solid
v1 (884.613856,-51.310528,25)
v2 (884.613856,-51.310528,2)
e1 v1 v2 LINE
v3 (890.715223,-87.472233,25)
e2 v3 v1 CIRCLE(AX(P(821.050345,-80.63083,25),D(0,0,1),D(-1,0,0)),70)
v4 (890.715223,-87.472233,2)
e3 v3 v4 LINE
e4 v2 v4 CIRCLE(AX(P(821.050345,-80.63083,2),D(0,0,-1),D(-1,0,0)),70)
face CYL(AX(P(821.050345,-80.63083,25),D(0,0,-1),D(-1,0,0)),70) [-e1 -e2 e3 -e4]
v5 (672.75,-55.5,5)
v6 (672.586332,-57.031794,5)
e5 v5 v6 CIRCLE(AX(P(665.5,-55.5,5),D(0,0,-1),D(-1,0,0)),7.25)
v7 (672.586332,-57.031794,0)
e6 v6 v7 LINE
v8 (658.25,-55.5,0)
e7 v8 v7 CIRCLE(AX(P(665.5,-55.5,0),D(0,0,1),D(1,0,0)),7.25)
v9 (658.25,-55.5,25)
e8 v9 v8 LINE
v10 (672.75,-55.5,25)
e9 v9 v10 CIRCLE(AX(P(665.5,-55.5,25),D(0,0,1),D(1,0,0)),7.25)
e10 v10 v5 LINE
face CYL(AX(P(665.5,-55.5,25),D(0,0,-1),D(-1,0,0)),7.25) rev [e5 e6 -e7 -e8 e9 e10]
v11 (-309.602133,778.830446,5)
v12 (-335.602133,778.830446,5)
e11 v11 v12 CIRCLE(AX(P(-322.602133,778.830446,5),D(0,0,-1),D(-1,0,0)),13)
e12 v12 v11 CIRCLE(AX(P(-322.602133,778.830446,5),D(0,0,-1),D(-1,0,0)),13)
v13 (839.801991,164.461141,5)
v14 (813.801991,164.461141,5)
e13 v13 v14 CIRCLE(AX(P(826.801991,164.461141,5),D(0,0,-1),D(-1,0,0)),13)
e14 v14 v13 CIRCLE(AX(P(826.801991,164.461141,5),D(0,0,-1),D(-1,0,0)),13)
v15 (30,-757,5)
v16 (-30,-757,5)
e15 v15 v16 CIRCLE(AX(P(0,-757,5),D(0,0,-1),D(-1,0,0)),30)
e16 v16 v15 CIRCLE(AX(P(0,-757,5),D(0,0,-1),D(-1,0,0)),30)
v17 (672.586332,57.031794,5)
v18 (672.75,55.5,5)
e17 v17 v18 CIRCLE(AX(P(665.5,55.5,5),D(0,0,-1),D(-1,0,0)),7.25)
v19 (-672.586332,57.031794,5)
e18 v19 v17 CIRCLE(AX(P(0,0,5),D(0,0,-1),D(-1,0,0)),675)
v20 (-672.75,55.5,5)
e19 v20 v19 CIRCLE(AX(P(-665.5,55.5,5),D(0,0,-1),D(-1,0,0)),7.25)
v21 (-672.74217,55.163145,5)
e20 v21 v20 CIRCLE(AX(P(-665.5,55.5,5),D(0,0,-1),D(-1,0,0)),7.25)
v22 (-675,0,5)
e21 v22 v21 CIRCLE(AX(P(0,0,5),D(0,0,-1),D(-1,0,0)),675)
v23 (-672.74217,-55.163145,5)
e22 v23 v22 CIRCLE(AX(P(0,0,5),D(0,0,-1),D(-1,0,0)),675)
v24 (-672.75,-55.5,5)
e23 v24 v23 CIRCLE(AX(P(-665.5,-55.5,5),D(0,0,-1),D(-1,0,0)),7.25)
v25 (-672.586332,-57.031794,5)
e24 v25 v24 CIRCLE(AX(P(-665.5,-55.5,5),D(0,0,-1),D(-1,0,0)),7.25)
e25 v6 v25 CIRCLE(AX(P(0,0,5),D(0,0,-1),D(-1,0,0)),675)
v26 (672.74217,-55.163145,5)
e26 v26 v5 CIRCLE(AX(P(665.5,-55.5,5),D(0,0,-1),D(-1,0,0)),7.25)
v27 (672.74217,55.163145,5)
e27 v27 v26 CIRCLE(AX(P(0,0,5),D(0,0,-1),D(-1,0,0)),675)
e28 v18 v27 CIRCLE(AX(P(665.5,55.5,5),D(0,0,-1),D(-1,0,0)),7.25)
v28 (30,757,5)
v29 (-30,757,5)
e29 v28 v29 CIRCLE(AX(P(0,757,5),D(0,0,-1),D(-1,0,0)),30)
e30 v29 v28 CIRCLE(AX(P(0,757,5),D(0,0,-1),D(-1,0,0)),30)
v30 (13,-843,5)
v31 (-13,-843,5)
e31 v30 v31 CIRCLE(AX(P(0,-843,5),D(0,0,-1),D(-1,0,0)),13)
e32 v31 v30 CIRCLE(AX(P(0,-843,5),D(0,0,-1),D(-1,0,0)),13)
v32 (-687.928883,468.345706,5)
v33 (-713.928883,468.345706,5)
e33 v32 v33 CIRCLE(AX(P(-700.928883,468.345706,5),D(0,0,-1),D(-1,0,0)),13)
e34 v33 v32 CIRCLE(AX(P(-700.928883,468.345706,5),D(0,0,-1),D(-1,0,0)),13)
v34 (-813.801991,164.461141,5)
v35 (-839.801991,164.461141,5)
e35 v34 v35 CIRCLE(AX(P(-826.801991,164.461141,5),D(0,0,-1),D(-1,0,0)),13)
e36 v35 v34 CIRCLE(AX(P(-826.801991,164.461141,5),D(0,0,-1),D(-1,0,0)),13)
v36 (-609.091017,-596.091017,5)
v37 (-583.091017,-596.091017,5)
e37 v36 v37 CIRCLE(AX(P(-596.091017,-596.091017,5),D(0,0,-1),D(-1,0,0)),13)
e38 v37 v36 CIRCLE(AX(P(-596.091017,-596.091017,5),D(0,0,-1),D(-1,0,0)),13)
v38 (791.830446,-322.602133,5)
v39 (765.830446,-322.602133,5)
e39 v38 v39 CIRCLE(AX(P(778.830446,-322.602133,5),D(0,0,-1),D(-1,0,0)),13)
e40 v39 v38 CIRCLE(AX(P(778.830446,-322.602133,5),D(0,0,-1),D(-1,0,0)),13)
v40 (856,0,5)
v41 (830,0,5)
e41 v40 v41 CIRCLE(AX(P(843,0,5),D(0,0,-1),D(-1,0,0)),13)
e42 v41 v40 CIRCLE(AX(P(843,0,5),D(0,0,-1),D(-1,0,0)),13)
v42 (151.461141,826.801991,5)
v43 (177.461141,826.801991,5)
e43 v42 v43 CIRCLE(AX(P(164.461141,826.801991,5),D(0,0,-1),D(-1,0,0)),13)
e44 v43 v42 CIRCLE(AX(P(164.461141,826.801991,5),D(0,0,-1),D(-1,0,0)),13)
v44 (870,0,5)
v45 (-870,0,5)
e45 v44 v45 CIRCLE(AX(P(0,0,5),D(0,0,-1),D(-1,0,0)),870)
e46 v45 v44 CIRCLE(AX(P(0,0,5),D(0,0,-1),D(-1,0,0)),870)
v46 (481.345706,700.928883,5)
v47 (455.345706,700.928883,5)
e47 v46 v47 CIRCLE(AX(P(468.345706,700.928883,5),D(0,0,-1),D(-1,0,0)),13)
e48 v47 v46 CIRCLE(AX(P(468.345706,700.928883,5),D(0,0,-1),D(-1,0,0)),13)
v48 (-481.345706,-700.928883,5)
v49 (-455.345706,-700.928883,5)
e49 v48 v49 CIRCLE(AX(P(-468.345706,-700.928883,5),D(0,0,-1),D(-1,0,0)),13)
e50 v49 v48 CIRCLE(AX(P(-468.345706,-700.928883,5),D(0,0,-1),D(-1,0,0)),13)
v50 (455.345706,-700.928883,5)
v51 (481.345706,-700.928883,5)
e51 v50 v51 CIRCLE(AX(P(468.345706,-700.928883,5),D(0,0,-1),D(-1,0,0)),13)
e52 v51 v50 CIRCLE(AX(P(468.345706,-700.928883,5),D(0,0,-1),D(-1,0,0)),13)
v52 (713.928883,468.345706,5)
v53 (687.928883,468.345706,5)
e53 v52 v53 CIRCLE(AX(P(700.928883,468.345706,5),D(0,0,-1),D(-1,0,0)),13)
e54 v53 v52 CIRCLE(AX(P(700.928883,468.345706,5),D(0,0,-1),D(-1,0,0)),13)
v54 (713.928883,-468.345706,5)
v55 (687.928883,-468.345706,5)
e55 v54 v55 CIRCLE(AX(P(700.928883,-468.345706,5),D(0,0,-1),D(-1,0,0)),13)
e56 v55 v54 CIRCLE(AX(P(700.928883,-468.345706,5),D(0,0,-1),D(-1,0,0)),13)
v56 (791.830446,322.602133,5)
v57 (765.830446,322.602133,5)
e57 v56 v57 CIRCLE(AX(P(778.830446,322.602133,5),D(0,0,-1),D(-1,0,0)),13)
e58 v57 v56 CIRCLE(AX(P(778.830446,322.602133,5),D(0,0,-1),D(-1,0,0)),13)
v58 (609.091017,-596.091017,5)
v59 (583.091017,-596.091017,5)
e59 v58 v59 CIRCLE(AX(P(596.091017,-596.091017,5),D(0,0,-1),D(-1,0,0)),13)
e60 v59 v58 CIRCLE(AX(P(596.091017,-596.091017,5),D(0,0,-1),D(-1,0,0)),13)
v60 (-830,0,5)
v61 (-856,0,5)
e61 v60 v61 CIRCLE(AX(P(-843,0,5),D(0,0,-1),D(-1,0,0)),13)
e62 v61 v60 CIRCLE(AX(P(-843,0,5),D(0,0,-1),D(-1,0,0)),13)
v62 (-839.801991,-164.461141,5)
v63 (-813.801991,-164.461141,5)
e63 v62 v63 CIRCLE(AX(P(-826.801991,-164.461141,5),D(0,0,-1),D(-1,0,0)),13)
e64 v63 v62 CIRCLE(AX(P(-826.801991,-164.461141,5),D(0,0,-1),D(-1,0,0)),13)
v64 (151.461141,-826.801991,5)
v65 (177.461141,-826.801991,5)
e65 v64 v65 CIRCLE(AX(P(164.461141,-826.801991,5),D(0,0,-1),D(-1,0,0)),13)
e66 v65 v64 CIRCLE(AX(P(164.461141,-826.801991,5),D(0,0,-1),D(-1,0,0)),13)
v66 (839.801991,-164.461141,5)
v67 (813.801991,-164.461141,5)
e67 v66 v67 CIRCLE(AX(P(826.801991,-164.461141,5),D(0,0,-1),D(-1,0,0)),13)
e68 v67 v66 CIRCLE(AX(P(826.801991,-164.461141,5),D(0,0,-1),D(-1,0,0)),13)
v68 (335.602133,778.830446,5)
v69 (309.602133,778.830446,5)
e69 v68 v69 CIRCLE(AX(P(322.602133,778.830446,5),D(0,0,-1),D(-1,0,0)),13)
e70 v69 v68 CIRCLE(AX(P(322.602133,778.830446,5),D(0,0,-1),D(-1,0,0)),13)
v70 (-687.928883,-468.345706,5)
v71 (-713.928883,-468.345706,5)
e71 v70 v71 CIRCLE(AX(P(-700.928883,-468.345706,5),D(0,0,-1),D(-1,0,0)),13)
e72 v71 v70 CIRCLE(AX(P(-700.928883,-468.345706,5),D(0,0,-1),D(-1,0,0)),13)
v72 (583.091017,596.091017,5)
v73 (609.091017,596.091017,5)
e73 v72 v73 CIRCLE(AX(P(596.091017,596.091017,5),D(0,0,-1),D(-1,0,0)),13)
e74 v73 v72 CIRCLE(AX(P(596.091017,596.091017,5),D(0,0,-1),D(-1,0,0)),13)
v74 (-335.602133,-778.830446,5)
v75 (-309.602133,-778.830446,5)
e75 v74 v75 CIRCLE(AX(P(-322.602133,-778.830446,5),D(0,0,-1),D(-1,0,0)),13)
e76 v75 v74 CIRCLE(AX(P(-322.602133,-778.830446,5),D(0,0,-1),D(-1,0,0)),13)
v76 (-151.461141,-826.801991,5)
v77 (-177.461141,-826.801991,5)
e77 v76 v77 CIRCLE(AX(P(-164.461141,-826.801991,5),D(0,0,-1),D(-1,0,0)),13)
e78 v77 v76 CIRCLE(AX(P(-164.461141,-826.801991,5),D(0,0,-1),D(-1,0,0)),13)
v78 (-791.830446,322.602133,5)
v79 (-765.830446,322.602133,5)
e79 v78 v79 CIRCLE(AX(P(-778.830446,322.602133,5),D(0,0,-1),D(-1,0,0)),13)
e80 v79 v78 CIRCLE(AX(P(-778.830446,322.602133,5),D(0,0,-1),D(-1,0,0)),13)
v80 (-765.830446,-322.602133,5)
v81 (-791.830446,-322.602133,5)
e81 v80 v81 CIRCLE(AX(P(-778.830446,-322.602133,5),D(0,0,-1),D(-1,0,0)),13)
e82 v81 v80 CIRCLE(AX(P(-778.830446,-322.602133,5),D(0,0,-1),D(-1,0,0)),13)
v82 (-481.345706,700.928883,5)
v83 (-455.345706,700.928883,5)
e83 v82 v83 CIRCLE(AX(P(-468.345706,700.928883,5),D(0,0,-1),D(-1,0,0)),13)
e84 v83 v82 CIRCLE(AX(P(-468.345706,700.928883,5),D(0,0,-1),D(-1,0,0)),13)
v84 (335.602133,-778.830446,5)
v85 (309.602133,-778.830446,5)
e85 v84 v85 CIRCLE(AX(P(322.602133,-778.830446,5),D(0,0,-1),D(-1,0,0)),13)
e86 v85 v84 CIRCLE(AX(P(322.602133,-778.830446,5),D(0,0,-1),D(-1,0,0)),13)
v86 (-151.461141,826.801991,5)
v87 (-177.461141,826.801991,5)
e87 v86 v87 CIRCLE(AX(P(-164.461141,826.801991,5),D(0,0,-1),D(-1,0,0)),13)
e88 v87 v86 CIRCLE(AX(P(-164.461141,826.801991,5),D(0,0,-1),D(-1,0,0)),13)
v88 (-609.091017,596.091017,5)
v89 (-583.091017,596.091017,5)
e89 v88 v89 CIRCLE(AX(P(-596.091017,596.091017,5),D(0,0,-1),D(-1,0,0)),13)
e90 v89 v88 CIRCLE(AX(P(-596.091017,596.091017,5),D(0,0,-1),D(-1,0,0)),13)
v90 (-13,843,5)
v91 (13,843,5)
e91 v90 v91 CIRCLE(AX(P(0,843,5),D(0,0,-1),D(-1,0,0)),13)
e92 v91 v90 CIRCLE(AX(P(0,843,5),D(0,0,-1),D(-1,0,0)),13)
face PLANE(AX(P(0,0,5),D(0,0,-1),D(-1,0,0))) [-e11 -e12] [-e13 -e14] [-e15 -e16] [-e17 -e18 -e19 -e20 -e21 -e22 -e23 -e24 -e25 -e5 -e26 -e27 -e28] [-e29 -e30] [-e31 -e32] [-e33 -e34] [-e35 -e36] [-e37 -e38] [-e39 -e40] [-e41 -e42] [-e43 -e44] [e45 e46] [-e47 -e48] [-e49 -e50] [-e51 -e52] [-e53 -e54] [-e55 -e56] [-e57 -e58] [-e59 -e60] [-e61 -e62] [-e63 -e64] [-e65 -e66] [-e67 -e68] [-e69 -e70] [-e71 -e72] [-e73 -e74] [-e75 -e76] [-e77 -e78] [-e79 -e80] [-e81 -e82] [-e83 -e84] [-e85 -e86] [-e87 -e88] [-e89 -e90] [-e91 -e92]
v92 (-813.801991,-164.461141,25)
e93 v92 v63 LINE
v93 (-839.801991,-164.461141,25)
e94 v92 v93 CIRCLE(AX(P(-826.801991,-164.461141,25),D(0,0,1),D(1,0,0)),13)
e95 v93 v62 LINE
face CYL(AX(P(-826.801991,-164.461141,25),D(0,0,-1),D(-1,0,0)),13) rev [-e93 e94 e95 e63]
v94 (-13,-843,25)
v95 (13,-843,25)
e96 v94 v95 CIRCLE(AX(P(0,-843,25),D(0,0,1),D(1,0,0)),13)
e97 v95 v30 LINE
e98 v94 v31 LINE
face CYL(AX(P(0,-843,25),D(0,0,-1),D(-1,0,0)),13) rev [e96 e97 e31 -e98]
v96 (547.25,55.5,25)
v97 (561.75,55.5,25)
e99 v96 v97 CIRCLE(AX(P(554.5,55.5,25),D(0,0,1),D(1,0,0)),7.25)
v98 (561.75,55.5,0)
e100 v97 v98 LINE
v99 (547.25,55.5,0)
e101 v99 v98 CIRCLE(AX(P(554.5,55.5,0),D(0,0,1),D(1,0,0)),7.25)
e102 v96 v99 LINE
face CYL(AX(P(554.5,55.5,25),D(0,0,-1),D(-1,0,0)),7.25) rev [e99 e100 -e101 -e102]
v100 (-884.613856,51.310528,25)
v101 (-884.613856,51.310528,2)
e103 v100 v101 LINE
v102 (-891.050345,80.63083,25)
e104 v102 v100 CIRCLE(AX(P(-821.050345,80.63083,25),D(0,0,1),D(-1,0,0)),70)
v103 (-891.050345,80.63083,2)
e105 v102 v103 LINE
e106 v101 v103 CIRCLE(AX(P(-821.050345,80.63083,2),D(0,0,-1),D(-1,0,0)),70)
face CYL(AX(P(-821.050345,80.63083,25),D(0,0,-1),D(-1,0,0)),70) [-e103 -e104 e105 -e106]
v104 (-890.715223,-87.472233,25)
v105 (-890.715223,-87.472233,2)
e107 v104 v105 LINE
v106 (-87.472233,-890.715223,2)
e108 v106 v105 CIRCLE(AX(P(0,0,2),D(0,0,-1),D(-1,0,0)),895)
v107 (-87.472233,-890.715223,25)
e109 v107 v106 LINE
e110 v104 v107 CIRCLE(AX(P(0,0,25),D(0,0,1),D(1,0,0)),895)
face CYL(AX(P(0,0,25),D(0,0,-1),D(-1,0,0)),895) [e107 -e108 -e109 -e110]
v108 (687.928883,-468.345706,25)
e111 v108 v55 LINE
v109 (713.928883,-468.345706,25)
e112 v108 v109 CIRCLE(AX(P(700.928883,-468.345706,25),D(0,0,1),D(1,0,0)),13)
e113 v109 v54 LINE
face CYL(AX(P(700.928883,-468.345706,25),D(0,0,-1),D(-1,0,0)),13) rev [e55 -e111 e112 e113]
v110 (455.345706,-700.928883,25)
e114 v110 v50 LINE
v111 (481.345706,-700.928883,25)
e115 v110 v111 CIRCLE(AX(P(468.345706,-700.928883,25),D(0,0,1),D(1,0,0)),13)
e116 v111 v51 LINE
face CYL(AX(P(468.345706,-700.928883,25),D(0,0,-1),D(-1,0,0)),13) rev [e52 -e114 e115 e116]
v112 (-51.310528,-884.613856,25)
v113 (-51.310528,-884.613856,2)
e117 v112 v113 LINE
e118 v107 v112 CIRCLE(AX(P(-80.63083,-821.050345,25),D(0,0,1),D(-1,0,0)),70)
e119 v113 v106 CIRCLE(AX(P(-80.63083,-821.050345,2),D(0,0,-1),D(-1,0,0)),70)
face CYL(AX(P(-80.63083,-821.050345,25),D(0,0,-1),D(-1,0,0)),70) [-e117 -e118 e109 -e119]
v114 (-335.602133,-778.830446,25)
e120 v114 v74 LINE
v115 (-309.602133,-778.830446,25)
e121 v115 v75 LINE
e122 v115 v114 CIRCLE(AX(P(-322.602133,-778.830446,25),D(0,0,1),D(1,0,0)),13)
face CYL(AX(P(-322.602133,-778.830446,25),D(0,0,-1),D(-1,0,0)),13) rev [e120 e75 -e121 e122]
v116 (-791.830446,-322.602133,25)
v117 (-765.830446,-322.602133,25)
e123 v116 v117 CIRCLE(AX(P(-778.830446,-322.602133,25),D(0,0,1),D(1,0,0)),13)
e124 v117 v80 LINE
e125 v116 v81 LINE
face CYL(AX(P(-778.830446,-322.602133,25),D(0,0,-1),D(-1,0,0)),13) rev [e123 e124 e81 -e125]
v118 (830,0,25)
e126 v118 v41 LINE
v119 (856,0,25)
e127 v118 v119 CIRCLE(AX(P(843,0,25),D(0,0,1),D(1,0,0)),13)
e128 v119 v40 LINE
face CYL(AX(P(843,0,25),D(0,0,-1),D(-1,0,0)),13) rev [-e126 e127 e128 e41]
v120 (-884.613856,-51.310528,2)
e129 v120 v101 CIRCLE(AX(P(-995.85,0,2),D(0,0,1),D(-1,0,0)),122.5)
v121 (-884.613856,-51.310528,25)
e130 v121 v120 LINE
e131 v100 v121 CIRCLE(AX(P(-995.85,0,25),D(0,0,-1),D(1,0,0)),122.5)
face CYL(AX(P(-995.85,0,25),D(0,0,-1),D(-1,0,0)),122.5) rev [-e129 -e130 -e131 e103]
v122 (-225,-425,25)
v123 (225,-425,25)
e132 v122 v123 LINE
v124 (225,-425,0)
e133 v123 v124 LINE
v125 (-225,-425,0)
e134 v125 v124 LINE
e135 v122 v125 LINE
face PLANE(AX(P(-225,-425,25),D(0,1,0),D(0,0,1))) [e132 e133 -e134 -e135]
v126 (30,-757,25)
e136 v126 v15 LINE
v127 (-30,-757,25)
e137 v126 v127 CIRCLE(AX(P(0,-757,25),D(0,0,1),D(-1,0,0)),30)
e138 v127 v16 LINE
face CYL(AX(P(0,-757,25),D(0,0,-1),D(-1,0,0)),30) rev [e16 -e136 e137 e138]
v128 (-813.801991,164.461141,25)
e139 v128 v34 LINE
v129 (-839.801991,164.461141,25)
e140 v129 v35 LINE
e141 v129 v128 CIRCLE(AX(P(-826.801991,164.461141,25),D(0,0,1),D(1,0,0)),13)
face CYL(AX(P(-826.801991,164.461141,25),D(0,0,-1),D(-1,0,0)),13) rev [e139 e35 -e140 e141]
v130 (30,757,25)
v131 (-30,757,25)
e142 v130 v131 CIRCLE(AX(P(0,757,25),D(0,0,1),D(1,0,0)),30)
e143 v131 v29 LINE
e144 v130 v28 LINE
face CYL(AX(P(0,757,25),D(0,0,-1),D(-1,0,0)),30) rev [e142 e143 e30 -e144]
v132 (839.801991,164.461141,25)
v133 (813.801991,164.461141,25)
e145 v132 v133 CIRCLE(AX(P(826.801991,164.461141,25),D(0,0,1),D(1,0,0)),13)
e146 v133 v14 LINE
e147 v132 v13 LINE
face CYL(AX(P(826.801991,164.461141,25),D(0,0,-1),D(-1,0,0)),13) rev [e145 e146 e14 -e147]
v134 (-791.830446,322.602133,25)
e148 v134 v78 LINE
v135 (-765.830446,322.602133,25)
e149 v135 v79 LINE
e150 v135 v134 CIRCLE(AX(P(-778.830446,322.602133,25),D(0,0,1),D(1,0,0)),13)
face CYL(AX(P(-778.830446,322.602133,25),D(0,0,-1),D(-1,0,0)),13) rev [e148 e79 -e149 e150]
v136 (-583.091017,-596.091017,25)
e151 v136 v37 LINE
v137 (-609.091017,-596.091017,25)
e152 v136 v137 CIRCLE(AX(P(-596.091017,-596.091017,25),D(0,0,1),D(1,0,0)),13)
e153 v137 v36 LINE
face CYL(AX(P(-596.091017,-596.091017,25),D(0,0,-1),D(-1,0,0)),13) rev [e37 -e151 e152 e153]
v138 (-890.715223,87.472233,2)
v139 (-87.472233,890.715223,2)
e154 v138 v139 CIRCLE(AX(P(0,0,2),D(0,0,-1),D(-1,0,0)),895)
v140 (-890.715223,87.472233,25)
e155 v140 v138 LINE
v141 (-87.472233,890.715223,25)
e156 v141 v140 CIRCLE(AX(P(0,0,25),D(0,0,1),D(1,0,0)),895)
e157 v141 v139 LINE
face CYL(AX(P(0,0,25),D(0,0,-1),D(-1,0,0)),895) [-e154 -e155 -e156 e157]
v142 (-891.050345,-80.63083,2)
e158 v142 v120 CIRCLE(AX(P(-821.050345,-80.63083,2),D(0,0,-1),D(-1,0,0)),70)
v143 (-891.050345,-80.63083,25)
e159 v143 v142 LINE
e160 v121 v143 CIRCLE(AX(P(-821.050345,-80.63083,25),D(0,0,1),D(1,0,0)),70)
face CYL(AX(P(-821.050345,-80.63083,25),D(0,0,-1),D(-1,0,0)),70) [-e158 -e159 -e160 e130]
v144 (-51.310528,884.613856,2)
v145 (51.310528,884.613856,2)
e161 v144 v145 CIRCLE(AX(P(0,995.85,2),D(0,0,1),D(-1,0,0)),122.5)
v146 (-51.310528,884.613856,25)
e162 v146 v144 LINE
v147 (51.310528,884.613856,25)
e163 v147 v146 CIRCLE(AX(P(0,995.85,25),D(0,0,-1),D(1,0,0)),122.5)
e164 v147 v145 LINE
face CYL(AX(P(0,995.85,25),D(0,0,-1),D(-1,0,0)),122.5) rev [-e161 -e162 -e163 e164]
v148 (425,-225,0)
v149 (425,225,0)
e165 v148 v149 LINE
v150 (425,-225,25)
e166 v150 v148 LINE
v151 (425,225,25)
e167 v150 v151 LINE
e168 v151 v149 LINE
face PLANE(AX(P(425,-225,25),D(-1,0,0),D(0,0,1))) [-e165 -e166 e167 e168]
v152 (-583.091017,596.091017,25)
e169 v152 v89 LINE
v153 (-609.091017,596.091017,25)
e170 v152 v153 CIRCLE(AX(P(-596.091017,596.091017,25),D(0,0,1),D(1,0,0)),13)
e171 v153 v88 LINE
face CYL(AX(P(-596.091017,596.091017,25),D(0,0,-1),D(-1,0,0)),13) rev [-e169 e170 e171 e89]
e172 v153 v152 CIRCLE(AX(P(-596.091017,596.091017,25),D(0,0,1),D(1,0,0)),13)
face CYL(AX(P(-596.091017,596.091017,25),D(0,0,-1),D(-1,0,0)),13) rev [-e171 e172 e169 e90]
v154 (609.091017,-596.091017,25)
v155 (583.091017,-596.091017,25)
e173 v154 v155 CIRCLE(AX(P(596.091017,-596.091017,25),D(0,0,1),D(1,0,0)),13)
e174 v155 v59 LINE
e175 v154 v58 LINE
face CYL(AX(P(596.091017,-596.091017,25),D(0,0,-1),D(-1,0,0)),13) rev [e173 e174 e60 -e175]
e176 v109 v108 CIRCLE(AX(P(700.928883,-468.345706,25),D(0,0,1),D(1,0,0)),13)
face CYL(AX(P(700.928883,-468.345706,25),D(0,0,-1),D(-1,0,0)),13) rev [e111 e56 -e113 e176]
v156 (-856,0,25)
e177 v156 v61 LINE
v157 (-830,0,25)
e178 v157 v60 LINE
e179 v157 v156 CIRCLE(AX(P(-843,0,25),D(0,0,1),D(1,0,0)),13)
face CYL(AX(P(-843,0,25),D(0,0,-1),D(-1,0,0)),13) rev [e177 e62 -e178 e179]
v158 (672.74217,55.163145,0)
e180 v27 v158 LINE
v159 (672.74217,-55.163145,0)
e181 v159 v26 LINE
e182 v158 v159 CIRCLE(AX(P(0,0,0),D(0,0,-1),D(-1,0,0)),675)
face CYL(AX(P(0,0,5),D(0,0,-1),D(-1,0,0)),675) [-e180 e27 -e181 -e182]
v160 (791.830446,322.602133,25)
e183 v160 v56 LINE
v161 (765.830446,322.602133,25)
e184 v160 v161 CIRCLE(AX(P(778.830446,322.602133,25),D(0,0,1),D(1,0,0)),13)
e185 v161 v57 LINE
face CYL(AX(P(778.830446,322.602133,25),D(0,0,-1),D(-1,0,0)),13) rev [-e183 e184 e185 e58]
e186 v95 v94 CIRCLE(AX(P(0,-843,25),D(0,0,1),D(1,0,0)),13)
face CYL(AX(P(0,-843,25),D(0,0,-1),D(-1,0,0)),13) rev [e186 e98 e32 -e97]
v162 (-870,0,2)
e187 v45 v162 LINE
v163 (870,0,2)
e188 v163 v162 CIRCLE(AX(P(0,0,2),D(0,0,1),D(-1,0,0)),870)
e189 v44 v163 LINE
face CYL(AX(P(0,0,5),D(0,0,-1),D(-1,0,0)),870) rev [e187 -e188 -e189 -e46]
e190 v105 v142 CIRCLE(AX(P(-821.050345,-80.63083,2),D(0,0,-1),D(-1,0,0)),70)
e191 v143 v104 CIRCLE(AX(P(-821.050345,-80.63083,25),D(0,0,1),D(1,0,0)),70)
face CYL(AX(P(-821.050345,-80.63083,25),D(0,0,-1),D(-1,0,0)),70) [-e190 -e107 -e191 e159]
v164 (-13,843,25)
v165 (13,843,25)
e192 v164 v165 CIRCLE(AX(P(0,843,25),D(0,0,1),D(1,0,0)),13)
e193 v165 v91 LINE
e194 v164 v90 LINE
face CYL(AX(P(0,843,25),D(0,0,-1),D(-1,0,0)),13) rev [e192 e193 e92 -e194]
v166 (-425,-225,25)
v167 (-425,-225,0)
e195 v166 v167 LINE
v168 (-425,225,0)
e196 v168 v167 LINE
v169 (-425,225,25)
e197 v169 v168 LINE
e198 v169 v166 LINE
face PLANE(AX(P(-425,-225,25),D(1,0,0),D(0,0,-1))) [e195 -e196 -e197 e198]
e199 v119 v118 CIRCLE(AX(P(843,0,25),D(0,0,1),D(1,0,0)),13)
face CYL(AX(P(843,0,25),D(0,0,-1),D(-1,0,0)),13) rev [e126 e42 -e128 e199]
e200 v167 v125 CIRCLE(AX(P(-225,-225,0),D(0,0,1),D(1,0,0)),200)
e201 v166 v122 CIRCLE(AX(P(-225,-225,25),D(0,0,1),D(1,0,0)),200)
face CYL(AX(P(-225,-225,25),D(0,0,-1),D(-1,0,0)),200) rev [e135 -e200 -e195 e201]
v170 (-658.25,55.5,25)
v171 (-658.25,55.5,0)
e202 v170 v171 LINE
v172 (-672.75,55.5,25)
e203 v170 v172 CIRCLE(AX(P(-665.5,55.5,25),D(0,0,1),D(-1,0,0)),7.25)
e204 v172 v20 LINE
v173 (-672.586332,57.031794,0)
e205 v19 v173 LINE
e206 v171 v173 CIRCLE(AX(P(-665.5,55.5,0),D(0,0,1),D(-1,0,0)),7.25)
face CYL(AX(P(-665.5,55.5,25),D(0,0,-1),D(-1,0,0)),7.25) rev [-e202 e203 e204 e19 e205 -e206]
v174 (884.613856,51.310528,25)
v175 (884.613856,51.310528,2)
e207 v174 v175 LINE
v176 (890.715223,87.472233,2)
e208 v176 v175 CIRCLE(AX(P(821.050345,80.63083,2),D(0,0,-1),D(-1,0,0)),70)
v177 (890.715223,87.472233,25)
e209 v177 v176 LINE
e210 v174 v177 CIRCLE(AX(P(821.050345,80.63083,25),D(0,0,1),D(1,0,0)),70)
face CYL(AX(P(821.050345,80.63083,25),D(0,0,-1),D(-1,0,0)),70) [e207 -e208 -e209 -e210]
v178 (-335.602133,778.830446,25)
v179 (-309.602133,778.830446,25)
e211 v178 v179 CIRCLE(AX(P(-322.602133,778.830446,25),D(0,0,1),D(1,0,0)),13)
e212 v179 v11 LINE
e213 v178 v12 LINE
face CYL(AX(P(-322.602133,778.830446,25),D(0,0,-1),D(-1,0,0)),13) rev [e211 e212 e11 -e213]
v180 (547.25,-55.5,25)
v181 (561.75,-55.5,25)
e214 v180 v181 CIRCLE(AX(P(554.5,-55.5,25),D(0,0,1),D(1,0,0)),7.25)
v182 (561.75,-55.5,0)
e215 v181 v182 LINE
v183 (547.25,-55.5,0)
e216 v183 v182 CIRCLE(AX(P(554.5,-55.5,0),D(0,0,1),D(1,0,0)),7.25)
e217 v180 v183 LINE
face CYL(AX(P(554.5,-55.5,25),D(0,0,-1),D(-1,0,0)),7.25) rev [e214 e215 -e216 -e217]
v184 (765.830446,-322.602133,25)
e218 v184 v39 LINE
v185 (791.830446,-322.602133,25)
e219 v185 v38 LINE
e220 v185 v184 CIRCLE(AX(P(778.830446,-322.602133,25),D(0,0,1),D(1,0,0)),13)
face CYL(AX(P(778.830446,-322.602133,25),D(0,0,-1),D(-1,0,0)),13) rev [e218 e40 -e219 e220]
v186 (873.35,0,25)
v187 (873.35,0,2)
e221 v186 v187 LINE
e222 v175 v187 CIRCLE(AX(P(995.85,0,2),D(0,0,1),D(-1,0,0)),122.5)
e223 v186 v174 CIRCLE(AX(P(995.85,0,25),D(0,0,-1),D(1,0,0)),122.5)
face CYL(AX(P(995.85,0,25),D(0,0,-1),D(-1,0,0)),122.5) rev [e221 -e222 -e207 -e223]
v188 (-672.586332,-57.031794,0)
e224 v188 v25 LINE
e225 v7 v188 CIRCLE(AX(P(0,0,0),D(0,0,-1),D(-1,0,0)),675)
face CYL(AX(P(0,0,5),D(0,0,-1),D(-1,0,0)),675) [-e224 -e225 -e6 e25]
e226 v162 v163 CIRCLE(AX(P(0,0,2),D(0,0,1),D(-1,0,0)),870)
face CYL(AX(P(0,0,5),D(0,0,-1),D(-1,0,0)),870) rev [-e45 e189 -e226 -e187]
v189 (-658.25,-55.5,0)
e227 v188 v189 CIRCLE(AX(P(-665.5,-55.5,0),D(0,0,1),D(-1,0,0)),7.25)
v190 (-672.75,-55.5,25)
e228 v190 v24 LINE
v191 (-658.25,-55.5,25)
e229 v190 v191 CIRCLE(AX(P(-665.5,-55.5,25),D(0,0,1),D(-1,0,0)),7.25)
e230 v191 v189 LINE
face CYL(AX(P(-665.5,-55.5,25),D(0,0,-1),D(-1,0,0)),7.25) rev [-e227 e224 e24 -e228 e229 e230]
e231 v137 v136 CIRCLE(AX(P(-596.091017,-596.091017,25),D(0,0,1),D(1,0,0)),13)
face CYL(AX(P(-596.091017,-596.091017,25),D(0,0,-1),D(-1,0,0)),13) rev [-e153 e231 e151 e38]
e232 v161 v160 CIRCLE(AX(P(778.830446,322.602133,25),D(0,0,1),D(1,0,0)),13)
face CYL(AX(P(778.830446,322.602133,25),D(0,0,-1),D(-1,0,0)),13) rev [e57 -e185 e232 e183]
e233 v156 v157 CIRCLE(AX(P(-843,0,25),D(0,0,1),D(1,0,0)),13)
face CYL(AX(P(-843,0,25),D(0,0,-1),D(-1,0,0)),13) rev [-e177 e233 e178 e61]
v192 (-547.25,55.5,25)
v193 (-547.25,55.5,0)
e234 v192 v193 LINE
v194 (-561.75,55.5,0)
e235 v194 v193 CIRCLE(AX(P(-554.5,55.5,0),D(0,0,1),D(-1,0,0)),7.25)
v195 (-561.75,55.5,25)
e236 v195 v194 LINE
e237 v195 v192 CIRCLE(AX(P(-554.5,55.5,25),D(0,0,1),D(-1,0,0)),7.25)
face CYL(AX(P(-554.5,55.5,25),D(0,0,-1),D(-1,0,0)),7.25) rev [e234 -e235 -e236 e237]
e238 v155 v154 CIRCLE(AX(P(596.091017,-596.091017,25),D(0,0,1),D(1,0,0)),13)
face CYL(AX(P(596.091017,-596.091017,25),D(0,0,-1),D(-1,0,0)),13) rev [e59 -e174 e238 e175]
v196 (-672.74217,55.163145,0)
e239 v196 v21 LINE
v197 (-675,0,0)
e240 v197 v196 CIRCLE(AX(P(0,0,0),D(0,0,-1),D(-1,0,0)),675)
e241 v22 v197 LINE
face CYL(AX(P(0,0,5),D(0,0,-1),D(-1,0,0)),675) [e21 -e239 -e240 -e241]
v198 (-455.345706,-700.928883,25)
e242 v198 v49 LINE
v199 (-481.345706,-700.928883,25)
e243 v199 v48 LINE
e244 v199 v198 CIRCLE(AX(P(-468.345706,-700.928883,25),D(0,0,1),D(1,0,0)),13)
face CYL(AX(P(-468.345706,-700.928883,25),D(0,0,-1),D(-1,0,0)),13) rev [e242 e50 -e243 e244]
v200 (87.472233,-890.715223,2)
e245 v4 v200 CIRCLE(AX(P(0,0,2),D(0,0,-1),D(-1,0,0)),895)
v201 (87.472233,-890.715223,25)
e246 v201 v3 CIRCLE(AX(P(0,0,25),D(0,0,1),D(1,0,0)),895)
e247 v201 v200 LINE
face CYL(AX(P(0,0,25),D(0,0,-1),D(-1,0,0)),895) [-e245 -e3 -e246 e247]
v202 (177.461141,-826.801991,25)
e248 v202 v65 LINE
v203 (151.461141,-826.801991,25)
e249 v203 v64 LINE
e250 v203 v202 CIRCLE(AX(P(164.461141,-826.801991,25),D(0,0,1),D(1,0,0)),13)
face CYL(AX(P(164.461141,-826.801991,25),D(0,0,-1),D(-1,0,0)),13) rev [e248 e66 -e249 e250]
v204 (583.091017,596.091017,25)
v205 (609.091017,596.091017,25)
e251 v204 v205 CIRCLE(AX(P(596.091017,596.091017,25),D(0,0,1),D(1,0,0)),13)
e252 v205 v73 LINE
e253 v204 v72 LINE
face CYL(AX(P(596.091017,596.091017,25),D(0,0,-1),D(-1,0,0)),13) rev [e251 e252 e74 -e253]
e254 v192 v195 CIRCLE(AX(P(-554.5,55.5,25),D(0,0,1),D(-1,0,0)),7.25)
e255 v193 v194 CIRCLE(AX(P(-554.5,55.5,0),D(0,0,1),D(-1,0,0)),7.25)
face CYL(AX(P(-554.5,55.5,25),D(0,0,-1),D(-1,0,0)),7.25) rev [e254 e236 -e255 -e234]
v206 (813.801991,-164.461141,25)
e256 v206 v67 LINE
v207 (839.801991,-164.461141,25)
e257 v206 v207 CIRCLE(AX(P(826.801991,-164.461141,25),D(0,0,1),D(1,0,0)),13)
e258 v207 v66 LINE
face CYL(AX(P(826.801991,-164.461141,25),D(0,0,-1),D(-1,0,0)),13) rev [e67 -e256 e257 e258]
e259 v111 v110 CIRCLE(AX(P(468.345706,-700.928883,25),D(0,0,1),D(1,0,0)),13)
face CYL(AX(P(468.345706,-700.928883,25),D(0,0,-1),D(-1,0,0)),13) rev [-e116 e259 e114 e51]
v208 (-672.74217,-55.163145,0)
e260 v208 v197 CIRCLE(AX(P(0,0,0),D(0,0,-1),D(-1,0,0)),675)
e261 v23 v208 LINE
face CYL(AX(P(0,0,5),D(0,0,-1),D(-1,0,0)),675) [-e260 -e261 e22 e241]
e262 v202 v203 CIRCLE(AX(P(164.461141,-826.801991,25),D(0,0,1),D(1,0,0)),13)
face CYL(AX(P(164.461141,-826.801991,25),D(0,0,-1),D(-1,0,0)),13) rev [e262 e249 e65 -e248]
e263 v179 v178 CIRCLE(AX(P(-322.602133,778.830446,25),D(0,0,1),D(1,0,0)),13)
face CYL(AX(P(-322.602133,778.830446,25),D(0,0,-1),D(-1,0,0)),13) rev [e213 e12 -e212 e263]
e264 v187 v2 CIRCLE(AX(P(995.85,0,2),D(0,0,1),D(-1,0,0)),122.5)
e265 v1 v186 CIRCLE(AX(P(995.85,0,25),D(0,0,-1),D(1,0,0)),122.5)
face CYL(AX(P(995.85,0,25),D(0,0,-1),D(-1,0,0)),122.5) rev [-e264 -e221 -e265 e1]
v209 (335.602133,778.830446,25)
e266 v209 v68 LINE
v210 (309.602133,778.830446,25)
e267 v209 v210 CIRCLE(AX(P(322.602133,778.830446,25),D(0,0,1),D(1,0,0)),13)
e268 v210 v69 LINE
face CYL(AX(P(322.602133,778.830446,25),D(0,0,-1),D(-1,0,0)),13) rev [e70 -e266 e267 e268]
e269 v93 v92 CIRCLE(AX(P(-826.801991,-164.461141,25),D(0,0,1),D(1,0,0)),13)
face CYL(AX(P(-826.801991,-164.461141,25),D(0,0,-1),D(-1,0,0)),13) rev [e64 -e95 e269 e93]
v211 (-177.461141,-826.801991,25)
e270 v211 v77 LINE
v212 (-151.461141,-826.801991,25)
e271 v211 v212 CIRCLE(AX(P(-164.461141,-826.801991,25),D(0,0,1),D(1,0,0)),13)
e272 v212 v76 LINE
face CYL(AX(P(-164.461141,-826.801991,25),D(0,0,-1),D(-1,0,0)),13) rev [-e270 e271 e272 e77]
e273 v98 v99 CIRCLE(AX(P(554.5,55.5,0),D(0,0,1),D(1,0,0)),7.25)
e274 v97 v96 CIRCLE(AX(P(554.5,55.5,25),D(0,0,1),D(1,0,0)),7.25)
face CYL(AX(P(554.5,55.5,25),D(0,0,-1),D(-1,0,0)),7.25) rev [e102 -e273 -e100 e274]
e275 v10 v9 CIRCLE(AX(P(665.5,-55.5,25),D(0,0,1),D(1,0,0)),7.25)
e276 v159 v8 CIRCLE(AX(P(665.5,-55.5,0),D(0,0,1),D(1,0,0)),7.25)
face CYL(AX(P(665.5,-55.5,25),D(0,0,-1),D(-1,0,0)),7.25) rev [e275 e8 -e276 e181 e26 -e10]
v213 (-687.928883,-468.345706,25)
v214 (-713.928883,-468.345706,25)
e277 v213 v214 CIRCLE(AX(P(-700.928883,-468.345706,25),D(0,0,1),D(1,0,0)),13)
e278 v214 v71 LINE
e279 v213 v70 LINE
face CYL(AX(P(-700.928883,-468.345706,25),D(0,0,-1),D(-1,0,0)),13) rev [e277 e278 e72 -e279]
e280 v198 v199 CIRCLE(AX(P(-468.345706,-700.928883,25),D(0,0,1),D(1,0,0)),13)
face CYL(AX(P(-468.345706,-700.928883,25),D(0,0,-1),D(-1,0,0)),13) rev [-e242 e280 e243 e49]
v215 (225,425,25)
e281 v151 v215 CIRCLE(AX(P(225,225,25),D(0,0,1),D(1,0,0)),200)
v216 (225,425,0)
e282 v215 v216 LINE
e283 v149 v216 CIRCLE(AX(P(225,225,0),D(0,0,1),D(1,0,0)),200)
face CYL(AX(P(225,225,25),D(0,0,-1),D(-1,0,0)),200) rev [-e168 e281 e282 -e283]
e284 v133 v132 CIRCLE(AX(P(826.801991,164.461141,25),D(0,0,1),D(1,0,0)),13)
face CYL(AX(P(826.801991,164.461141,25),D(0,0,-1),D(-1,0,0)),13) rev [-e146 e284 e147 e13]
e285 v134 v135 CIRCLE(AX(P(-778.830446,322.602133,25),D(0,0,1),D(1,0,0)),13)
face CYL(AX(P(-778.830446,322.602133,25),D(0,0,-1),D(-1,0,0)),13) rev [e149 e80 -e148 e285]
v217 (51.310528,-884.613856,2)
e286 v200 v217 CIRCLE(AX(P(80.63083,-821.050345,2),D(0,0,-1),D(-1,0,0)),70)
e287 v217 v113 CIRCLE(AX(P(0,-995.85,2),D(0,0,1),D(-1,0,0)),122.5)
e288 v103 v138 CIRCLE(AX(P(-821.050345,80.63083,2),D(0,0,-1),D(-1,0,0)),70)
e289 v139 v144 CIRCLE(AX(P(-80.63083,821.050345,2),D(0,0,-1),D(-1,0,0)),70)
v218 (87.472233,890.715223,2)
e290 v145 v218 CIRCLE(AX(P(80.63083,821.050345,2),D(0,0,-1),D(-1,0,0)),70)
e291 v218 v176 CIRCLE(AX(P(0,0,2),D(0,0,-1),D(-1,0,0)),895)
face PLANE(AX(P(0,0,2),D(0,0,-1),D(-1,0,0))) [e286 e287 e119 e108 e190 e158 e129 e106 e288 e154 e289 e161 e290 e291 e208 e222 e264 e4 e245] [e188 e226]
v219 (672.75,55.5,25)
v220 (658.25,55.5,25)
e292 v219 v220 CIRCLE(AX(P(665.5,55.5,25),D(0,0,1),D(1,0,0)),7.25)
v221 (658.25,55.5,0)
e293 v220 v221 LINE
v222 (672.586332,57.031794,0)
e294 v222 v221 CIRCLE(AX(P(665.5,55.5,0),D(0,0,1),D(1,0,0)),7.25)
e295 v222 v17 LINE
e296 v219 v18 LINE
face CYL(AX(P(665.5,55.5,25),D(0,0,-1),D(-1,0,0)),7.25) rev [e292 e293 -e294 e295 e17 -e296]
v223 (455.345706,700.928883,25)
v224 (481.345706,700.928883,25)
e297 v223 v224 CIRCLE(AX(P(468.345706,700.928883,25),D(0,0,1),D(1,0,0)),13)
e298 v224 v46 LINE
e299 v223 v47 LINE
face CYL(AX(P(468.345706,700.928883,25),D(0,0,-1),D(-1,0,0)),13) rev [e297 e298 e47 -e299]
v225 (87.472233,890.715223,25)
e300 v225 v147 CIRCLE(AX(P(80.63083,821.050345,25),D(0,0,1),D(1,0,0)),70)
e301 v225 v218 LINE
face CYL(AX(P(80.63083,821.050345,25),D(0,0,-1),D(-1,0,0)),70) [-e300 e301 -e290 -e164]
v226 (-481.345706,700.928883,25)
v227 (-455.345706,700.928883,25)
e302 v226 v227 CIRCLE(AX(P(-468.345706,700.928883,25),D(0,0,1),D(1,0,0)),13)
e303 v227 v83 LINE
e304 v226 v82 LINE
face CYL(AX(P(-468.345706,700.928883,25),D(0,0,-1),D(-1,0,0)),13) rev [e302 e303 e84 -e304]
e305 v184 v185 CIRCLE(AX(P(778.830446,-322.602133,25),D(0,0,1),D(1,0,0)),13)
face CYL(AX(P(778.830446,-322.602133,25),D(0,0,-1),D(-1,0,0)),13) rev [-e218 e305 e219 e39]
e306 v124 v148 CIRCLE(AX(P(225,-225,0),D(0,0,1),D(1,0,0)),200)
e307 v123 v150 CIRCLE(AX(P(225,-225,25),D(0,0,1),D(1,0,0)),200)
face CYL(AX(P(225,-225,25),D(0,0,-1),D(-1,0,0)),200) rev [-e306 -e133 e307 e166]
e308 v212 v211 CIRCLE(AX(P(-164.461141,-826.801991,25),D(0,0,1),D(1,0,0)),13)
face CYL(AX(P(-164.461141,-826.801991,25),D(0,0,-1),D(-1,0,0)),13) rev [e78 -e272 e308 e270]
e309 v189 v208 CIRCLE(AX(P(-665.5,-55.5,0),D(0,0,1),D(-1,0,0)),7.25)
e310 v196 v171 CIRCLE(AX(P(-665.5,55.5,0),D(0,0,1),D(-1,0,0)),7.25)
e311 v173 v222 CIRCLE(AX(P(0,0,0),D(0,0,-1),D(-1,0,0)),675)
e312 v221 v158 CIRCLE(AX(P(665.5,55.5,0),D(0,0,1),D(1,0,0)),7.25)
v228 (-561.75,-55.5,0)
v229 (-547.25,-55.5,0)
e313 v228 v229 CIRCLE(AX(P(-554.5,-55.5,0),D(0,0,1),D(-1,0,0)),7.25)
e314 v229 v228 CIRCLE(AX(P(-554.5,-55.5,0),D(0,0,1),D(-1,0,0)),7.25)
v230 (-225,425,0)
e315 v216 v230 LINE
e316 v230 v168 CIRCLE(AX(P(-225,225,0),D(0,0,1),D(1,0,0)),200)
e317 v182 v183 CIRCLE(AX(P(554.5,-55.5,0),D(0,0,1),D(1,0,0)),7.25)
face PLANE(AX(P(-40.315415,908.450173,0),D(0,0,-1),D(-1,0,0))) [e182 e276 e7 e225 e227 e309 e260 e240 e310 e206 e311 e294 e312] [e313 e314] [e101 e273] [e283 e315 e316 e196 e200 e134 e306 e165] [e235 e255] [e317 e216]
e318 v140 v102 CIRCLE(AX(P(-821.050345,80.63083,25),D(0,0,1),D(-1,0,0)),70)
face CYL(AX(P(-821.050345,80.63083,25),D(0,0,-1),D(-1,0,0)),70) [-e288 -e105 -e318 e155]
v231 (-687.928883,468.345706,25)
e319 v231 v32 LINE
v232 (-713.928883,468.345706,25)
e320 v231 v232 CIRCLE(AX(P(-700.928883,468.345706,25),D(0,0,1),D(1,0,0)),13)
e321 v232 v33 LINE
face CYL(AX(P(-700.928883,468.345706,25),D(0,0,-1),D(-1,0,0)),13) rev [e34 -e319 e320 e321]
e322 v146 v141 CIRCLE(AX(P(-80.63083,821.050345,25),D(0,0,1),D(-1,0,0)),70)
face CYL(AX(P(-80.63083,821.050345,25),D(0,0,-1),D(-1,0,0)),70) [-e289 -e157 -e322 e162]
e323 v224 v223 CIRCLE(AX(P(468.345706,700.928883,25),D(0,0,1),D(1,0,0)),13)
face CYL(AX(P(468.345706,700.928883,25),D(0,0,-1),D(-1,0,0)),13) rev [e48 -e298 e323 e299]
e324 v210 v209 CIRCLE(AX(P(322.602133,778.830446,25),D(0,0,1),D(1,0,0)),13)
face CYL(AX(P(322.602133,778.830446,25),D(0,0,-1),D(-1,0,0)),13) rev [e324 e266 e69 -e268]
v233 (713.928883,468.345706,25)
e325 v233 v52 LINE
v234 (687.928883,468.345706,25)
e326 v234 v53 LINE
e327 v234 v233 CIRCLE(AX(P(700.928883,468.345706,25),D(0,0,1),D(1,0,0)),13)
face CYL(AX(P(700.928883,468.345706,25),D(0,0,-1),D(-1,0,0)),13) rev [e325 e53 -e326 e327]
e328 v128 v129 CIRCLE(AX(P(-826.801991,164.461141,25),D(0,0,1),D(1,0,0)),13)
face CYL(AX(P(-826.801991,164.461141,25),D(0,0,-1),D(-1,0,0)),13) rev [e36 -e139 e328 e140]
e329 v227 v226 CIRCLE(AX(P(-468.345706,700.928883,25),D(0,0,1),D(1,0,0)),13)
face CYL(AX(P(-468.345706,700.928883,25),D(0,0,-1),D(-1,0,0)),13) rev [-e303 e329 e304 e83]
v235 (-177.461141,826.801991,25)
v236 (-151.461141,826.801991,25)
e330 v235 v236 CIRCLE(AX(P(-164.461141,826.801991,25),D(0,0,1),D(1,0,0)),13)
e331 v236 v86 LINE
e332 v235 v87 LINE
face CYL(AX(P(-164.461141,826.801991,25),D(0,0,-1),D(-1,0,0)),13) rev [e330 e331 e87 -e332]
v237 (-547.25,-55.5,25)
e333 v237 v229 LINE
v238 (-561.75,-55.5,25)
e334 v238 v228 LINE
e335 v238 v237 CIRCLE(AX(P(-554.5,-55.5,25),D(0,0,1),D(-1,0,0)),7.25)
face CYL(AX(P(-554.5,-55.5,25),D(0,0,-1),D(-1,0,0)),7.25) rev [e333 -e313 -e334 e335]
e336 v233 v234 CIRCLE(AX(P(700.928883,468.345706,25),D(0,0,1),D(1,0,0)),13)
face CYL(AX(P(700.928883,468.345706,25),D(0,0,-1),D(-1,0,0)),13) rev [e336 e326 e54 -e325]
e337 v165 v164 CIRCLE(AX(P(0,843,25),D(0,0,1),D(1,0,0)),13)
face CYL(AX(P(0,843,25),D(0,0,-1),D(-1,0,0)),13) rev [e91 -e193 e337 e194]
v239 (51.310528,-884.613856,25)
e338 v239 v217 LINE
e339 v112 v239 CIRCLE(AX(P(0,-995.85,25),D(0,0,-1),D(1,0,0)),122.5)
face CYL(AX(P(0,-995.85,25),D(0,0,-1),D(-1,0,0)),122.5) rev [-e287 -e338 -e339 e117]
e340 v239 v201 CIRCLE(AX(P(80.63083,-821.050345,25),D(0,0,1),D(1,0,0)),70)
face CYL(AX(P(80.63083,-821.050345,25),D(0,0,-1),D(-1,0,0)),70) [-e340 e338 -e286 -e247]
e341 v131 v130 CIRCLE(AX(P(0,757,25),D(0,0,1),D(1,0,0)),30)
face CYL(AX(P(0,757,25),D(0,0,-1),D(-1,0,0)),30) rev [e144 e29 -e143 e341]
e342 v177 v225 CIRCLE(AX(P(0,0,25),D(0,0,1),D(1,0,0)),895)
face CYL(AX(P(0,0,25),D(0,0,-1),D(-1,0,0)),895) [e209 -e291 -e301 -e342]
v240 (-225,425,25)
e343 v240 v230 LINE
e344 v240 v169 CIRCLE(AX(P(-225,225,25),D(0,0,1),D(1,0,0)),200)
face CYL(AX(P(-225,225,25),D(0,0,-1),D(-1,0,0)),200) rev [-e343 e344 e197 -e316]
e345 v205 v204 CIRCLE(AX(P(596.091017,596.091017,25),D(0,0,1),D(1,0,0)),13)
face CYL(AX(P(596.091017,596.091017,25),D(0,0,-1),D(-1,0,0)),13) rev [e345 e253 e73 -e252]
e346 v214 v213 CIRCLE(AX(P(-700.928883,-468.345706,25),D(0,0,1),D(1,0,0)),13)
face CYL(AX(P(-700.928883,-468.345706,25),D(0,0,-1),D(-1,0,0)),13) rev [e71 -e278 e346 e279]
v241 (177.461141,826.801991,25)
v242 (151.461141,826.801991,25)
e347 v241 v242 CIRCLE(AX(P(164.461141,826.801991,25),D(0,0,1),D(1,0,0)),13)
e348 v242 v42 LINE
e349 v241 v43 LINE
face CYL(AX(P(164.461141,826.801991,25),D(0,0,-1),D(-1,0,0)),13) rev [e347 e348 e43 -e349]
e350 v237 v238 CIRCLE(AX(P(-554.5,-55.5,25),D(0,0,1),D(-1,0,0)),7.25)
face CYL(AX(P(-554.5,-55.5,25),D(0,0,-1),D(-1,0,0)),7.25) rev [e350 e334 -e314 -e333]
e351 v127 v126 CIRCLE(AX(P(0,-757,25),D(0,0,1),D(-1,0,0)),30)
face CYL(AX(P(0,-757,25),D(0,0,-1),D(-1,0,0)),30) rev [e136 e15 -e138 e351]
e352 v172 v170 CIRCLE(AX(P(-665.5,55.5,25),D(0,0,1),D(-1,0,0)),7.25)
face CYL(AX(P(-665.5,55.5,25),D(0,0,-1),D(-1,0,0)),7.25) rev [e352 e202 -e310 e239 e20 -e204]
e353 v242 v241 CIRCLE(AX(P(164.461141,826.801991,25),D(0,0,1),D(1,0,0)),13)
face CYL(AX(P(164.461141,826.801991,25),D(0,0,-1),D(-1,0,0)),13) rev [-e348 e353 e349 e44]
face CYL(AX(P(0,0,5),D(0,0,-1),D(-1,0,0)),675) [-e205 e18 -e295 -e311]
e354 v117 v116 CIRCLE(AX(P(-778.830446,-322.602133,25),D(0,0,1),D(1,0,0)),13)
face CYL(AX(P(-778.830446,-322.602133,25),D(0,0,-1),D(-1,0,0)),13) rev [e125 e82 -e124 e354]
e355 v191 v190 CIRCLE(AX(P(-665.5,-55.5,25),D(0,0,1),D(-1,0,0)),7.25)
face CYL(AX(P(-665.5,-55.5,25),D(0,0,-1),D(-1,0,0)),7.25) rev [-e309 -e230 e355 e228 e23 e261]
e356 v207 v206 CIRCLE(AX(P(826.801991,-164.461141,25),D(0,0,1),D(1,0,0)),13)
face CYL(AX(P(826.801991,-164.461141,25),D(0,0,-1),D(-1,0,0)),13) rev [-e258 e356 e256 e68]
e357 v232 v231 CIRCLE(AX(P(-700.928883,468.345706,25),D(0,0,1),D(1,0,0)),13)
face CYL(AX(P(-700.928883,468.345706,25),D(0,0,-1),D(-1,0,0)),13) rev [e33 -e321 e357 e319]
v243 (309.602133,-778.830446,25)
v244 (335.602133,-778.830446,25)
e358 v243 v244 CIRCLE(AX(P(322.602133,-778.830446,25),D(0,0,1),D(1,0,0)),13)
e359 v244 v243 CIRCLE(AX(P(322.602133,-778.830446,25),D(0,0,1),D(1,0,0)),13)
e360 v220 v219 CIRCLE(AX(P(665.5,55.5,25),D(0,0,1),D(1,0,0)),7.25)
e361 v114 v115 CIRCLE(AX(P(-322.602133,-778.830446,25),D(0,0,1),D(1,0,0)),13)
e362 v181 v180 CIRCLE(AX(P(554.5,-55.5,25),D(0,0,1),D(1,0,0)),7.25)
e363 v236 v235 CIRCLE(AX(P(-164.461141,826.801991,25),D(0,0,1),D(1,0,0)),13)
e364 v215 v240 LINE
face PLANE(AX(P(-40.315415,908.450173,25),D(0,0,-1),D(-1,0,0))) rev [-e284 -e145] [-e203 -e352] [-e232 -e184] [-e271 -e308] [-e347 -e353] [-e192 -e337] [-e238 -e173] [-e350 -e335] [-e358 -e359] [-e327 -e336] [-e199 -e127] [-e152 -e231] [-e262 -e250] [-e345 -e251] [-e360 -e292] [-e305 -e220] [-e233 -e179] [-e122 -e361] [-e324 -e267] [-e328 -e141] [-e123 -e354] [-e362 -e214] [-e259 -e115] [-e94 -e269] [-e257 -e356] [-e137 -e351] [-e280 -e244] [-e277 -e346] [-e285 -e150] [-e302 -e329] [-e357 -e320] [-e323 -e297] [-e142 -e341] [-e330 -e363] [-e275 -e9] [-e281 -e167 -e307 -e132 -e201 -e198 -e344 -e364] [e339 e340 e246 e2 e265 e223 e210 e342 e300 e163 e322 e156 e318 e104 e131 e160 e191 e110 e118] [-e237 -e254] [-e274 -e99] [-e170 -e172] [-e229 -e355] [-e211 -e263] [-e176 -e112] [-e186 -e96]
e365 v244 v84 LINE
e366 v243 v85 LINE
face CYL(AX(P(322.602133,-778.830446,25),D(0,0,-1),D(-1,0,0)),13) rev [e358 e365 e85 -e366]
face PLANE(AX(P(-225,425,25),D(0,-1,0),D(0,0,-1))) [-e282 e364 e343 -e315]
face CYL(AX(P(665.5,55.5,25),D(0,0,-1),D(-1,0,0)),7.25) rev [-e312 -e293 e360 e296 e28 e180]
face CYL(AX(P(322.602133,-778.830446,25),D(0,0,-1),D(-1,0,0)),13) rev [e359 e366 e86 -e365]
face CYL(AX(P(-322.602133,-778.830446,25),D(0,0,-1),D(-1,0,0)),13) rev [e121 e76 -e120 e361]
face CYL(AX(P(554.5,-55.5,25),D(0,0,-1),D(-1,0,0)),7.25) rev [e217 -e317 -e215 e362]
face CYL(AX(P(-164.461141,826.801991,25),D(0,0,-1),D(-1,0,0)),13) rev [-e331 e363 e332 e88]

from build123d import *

# Parameters (mm, degrees)
SKETCH1_R           = 13
SKETCH1_R_2         = 30
SKETCH1_R_3         = 7.25
BOSS_EXTRUDE1_DEPTH = 25
SKETCH2_R           = 870
SKETCH2_R_2         = 675
CUT_EXTRUDE1_DEPTH  = 5
SKETCH3_R           = 1126.547936792
SKETCH3_R_2         = 762.256112449
CUT_EXTRUDE2_DEPTH  = 2


with BuildPart() as part:
    # Sketch1 → Boss-Extrude1 (new body)
    with BuildSketch(Plane.XY):
        with BuildLine():
            ThreePointArc((-87.472233281, 890.715222956), (-632.860569162, 632.860569162), (-890.715222956, 87.472233281))
            ThreePointArc((-890.715222956, 87.472233281), (-890.074747514, 68.984719363), (-884.613856025, 51.310527902))
            ThreePointArc((-884.613856025, 51.310527902), (-873.35, 0), (-884.613856025, -51.310527902))
            ThreePointArc((-884.613856025, -51.310527902), (-890.074747514, -68.984719363), (-890.715222956, -87.472233281))
            ThreePointArc((-890.715222956, -87.472233281), (-632.860569162, -632.860569162), (-87.472233281, -890.715222956))
            ThreePointArc((-87.472233281, -890.715222956), (-68.984719363, -890.074747514), (-51.310527902, -884.613856025))
            ThreePointArc((-51.310527902, -884.613856025), (0, -873.35), (51.310527902, -884.613856025))
            ThreePointArc((51.310527902, -884.613856025), (68.984719363, -890.074747514), (87.472233281, -890.715222956))
            ThreePointArc((87.472233281, -890.715222956), (632.860569162, -632.860569162), (890.715222956, -87.472233281))
            ThreePointArc((890.715222956, -87.472233281), (890.074747514, -68.984719363), (884.613856025, -51.310527902))
            ThreePointArc((884.613856025, -51.310527902), (873.35, 0), (884.613856025, 51.310527902))
            ThreePointArc((884.613856025, 51.310527902), (890.074747514, 68.984719363), (890.715222956, 87.472233281))
            ThreePointArc((890.715222956, 87.472233281), (632.860569162, 632.860569162), (87.472233281, 890.715222956))
            ThreePointArc((87.472233281, 890.715222956), (68.984719363, 890.074747514), (51.310527902, 884.613856025))
            ThreePointArc((51.310527902, 884.613856025), (0, 873.35), (-51.310527902, 884.613856025))
            ThreePointArc((-51.310527902, 884.613856025), (-68.984719363, 890.074747514), (-87.472233281, 890.715222956))
        make_face()
        with Locations((0, 843)):
            Circle(SKETCH1_R, mode=Mode.SUBTRACT)
        with Locations((0, 757)):
            Circle(SKETCH1_R_2, mode=Mode.SUBTRACT)
        with Locations((554.5, 55.5)):
            Circle(SKETCH1_R_3, mode=Mode.SUBTRACT)
        with Locations((665.5, 55.5)):
            Circle(SKETCH1_R_3, mode=Mode.SUBTRACT)
        with Locations((665.5, -55.5)):
            Circle(SKETCH1_R_3, mode=Mode.SUBTRACT)
        with Locations((554.5, -55.5)):
            Circle(SKETCH1_R_3, mode=Mode.SUBTRACT)
        with Locations(Location((0, -757, 0), (0, 0, 180))):
            Circle(SKETCH1_R_2, mode=Mode.SUBTRACT)
        with Locations(Location((-665.5, -55.5, 0), (0, 0, 180))):
            Circle(SKETCH1_R_3, mode=Mode.SUBTRACT)
        with Locations(Location((-554.5, -55.5, 0), (0, 0, 180))):
            Circle(SKETCH1_R_3, mode=Mode.SUBTRACT)
        with Locations(Location((-665.5, 55.5, 0), (0, 0, 180))):
            Circle(SKETCH1_R_3, mode=Mode.SUBTRACT)
        with Locations(Location((-554.5, 55.5, 0), (0, 0, 180))):
            Circle(SKETCH1_R_3, mode=Mode.SUBTRACT)
        with Locations((164.46114146, 826.80199138)):
            Circle(SKETCH1_R, mode=Mode.SUBTRACT)
        with Locations((322.602133484, 778.830445907)):
            Circle(SKETCH1_R, mode=Mode.SUBTRACT)
        with Locations((468.345706436, 700.928883171)):
            Circle(SKETCH1_R, mode=Mode.SUBTRACT)
        with Locations((596.09101654, 596.09101654)):
            Circle(SKETCH1_R, mode=Mode.SUBTRACT)
        with Locations((700.928883171, 468.345706436)):
            Circle(SKETCH1_R, mode=Mode.SUBTRACT)
        with Locations((778.830445907, 322.602133484)):
            Circle(SKETCH1_R, mode=Mode.SUBTRACT)
        with Locations((826.80199138, 164.46114146)):
            Circle(SKETCH1_R, mode=Mode.SUBTRACT)
        with Locations((843, 0)):
            Circle(SKETCH1_R, mode=Mode.SUBTRACT)
        with Locations((826.80199138, -164.46114146)):
            Circle(SKETCH1_R, mode=Mode.SUBTRACT)
        with Locations((778.830445907, -322.602133484)):
            Circle(SKETCH1_R, mode=Mode.SUBTRACT)
        with Locations((700.928883171, -468.345706436)):
            Circle(SKETCH1_R, mode=Mode.SUBTRACT)
        with Locations((596.09101654, -596.09101654)):
            Circle(SKETCH1_R, mode=Mode.SUBTRACT)
        with Locations((468.345706436, -700.928883171)):
            Circle(SKETCH1_R, mode=Mode.SUBTRACT)
        with Locations((322.602133484, -778.830445907)):
            Circle(SKETCH1_R, mode=Mode.SUBTRACT)
        with Locations((164.46114146, -826.80199138)):
            Circle(SKETCH1_R, mode=Mode.SUBTRACT)
        with Locations((0, -843)):
            Circle(SKETCH1_R, mode=Mode.SUBTRACT)
        with Locations((-164.46114146, -826.80199138)):
            Circle(SKETCH1_R, mode=Mode.SUBTRACT)
        with Locations((-322.602133484, -778.830445907)):
            Circle(SKETCH1_R, mode=Mode.SUBTRACT)
        with Locations((-468.345706436, -700.928883171)):
            Circle(SKETCH1_R, mode=Mode.SUBTRACT)
        with Locations((-596.09101654, -596.09101654)):
            Circle(SKETCH1_R, mode=Mode.SUBTRACT)
        with Locations((-700.928883171, -468.345706436)):
            Circle(SKETCH1_R, mode=Mode.SUBTRACT)
        with Locations((-778.830445907, -322.602133484)):
            Circle(SKETCH1_R, mode=Mode.SUBTRACT)
        with Locations((-826.80199138, -164.46114146)):
            Circle(SKETCH1_R, mode=Mode.SUBTRACT)
        with Locations((-843, 0)):
            Circle(SKETCH1_R, mode=Mode.SUBTRACT)
        with Locations((-826.80199138, 164.46114146)):
            Circle(SKETCH1_R, mode=Mode.SUBTRACT)
        with Locations((-778.830445907, 322.602133484)):
            Circle(SKETCH1_R, mode=Mode.SUBTRACT)
        with Locations((-700.928883171, 468.345706436)):
            Circle(SKETCH1_R, mode=Mode.SUBTRACT)
        with Locations((-596.09101654, 596.09101654)):
            Circle(SKETCH1_R, mode=Mode.SUBTRACT)
        with Locations((-468.345706436, 700.928883171)):
            Circle(SKETCH1_R, mode=Mode.SUBTRACT)
        with Locations((-322.602133484, 778.830445907)):
            Circle(SKETCH1_R, mode=Mode.SUBTRACT)
        with Locations((-164.46114146, 826.80199138)):
            Circle(SKETCH1_R, mode=Mode.SUBTRACT)
        with BuildLine():
            Line((-225, -425), (225, -425))
            ThreePointArc((225, -425), (366.421356237, -366.421356237), (425, -225))
            Line((425, -225), (425, 225))
            ThreePointArc((425, 225), (366.421356237, 366.421356237), (225, 425))
            Line((225, 425), (-225, 425))
            ThreePointArc((-225, 425), (-366.421356237, 366.421356237), (-425, 225))
            Line((-425, 225), (-425, -225))
            ThreePointArc((-425, -225), (-366.421356237, -366.421356237), (-225, -425))
        make_face(mode=Mode.SUBTRACT)
    extrude(amount=BOSS_EXTRUDE1_DEPTH)

    # Sketch2 → Cut-Extrude1 (cut)
    with BuildSketch(Plane(origin=(0, 0, 0), x_dir=(-1, 0, 0), z_dir=(0, 0, -1))):
        Circle(SKETCH2_R)
        Circle(SKETCH2_R_2, mode=Mode.SUBTRACT)
    extrude(amount=-CUT_EXTRUDE1_DEPTH, mode=Mode.SUBTRACT)

    # Sketch3 → Cut-Extrude2 (cut)
    with BuildSketch(Plane(origin=(0, 0, 0), x_dir=(-1, 0, 0), z_dir=(0, 0, -1))):
        Circle(SKETCH3_R)
        Circle(SKETCH3_R_2, mode=Mode.SUBTRACT)
    extrude(amount=-CUT_EXTRUDE2_DEPTH, mode=Mode.SUBTRACT)


solid = part.part
